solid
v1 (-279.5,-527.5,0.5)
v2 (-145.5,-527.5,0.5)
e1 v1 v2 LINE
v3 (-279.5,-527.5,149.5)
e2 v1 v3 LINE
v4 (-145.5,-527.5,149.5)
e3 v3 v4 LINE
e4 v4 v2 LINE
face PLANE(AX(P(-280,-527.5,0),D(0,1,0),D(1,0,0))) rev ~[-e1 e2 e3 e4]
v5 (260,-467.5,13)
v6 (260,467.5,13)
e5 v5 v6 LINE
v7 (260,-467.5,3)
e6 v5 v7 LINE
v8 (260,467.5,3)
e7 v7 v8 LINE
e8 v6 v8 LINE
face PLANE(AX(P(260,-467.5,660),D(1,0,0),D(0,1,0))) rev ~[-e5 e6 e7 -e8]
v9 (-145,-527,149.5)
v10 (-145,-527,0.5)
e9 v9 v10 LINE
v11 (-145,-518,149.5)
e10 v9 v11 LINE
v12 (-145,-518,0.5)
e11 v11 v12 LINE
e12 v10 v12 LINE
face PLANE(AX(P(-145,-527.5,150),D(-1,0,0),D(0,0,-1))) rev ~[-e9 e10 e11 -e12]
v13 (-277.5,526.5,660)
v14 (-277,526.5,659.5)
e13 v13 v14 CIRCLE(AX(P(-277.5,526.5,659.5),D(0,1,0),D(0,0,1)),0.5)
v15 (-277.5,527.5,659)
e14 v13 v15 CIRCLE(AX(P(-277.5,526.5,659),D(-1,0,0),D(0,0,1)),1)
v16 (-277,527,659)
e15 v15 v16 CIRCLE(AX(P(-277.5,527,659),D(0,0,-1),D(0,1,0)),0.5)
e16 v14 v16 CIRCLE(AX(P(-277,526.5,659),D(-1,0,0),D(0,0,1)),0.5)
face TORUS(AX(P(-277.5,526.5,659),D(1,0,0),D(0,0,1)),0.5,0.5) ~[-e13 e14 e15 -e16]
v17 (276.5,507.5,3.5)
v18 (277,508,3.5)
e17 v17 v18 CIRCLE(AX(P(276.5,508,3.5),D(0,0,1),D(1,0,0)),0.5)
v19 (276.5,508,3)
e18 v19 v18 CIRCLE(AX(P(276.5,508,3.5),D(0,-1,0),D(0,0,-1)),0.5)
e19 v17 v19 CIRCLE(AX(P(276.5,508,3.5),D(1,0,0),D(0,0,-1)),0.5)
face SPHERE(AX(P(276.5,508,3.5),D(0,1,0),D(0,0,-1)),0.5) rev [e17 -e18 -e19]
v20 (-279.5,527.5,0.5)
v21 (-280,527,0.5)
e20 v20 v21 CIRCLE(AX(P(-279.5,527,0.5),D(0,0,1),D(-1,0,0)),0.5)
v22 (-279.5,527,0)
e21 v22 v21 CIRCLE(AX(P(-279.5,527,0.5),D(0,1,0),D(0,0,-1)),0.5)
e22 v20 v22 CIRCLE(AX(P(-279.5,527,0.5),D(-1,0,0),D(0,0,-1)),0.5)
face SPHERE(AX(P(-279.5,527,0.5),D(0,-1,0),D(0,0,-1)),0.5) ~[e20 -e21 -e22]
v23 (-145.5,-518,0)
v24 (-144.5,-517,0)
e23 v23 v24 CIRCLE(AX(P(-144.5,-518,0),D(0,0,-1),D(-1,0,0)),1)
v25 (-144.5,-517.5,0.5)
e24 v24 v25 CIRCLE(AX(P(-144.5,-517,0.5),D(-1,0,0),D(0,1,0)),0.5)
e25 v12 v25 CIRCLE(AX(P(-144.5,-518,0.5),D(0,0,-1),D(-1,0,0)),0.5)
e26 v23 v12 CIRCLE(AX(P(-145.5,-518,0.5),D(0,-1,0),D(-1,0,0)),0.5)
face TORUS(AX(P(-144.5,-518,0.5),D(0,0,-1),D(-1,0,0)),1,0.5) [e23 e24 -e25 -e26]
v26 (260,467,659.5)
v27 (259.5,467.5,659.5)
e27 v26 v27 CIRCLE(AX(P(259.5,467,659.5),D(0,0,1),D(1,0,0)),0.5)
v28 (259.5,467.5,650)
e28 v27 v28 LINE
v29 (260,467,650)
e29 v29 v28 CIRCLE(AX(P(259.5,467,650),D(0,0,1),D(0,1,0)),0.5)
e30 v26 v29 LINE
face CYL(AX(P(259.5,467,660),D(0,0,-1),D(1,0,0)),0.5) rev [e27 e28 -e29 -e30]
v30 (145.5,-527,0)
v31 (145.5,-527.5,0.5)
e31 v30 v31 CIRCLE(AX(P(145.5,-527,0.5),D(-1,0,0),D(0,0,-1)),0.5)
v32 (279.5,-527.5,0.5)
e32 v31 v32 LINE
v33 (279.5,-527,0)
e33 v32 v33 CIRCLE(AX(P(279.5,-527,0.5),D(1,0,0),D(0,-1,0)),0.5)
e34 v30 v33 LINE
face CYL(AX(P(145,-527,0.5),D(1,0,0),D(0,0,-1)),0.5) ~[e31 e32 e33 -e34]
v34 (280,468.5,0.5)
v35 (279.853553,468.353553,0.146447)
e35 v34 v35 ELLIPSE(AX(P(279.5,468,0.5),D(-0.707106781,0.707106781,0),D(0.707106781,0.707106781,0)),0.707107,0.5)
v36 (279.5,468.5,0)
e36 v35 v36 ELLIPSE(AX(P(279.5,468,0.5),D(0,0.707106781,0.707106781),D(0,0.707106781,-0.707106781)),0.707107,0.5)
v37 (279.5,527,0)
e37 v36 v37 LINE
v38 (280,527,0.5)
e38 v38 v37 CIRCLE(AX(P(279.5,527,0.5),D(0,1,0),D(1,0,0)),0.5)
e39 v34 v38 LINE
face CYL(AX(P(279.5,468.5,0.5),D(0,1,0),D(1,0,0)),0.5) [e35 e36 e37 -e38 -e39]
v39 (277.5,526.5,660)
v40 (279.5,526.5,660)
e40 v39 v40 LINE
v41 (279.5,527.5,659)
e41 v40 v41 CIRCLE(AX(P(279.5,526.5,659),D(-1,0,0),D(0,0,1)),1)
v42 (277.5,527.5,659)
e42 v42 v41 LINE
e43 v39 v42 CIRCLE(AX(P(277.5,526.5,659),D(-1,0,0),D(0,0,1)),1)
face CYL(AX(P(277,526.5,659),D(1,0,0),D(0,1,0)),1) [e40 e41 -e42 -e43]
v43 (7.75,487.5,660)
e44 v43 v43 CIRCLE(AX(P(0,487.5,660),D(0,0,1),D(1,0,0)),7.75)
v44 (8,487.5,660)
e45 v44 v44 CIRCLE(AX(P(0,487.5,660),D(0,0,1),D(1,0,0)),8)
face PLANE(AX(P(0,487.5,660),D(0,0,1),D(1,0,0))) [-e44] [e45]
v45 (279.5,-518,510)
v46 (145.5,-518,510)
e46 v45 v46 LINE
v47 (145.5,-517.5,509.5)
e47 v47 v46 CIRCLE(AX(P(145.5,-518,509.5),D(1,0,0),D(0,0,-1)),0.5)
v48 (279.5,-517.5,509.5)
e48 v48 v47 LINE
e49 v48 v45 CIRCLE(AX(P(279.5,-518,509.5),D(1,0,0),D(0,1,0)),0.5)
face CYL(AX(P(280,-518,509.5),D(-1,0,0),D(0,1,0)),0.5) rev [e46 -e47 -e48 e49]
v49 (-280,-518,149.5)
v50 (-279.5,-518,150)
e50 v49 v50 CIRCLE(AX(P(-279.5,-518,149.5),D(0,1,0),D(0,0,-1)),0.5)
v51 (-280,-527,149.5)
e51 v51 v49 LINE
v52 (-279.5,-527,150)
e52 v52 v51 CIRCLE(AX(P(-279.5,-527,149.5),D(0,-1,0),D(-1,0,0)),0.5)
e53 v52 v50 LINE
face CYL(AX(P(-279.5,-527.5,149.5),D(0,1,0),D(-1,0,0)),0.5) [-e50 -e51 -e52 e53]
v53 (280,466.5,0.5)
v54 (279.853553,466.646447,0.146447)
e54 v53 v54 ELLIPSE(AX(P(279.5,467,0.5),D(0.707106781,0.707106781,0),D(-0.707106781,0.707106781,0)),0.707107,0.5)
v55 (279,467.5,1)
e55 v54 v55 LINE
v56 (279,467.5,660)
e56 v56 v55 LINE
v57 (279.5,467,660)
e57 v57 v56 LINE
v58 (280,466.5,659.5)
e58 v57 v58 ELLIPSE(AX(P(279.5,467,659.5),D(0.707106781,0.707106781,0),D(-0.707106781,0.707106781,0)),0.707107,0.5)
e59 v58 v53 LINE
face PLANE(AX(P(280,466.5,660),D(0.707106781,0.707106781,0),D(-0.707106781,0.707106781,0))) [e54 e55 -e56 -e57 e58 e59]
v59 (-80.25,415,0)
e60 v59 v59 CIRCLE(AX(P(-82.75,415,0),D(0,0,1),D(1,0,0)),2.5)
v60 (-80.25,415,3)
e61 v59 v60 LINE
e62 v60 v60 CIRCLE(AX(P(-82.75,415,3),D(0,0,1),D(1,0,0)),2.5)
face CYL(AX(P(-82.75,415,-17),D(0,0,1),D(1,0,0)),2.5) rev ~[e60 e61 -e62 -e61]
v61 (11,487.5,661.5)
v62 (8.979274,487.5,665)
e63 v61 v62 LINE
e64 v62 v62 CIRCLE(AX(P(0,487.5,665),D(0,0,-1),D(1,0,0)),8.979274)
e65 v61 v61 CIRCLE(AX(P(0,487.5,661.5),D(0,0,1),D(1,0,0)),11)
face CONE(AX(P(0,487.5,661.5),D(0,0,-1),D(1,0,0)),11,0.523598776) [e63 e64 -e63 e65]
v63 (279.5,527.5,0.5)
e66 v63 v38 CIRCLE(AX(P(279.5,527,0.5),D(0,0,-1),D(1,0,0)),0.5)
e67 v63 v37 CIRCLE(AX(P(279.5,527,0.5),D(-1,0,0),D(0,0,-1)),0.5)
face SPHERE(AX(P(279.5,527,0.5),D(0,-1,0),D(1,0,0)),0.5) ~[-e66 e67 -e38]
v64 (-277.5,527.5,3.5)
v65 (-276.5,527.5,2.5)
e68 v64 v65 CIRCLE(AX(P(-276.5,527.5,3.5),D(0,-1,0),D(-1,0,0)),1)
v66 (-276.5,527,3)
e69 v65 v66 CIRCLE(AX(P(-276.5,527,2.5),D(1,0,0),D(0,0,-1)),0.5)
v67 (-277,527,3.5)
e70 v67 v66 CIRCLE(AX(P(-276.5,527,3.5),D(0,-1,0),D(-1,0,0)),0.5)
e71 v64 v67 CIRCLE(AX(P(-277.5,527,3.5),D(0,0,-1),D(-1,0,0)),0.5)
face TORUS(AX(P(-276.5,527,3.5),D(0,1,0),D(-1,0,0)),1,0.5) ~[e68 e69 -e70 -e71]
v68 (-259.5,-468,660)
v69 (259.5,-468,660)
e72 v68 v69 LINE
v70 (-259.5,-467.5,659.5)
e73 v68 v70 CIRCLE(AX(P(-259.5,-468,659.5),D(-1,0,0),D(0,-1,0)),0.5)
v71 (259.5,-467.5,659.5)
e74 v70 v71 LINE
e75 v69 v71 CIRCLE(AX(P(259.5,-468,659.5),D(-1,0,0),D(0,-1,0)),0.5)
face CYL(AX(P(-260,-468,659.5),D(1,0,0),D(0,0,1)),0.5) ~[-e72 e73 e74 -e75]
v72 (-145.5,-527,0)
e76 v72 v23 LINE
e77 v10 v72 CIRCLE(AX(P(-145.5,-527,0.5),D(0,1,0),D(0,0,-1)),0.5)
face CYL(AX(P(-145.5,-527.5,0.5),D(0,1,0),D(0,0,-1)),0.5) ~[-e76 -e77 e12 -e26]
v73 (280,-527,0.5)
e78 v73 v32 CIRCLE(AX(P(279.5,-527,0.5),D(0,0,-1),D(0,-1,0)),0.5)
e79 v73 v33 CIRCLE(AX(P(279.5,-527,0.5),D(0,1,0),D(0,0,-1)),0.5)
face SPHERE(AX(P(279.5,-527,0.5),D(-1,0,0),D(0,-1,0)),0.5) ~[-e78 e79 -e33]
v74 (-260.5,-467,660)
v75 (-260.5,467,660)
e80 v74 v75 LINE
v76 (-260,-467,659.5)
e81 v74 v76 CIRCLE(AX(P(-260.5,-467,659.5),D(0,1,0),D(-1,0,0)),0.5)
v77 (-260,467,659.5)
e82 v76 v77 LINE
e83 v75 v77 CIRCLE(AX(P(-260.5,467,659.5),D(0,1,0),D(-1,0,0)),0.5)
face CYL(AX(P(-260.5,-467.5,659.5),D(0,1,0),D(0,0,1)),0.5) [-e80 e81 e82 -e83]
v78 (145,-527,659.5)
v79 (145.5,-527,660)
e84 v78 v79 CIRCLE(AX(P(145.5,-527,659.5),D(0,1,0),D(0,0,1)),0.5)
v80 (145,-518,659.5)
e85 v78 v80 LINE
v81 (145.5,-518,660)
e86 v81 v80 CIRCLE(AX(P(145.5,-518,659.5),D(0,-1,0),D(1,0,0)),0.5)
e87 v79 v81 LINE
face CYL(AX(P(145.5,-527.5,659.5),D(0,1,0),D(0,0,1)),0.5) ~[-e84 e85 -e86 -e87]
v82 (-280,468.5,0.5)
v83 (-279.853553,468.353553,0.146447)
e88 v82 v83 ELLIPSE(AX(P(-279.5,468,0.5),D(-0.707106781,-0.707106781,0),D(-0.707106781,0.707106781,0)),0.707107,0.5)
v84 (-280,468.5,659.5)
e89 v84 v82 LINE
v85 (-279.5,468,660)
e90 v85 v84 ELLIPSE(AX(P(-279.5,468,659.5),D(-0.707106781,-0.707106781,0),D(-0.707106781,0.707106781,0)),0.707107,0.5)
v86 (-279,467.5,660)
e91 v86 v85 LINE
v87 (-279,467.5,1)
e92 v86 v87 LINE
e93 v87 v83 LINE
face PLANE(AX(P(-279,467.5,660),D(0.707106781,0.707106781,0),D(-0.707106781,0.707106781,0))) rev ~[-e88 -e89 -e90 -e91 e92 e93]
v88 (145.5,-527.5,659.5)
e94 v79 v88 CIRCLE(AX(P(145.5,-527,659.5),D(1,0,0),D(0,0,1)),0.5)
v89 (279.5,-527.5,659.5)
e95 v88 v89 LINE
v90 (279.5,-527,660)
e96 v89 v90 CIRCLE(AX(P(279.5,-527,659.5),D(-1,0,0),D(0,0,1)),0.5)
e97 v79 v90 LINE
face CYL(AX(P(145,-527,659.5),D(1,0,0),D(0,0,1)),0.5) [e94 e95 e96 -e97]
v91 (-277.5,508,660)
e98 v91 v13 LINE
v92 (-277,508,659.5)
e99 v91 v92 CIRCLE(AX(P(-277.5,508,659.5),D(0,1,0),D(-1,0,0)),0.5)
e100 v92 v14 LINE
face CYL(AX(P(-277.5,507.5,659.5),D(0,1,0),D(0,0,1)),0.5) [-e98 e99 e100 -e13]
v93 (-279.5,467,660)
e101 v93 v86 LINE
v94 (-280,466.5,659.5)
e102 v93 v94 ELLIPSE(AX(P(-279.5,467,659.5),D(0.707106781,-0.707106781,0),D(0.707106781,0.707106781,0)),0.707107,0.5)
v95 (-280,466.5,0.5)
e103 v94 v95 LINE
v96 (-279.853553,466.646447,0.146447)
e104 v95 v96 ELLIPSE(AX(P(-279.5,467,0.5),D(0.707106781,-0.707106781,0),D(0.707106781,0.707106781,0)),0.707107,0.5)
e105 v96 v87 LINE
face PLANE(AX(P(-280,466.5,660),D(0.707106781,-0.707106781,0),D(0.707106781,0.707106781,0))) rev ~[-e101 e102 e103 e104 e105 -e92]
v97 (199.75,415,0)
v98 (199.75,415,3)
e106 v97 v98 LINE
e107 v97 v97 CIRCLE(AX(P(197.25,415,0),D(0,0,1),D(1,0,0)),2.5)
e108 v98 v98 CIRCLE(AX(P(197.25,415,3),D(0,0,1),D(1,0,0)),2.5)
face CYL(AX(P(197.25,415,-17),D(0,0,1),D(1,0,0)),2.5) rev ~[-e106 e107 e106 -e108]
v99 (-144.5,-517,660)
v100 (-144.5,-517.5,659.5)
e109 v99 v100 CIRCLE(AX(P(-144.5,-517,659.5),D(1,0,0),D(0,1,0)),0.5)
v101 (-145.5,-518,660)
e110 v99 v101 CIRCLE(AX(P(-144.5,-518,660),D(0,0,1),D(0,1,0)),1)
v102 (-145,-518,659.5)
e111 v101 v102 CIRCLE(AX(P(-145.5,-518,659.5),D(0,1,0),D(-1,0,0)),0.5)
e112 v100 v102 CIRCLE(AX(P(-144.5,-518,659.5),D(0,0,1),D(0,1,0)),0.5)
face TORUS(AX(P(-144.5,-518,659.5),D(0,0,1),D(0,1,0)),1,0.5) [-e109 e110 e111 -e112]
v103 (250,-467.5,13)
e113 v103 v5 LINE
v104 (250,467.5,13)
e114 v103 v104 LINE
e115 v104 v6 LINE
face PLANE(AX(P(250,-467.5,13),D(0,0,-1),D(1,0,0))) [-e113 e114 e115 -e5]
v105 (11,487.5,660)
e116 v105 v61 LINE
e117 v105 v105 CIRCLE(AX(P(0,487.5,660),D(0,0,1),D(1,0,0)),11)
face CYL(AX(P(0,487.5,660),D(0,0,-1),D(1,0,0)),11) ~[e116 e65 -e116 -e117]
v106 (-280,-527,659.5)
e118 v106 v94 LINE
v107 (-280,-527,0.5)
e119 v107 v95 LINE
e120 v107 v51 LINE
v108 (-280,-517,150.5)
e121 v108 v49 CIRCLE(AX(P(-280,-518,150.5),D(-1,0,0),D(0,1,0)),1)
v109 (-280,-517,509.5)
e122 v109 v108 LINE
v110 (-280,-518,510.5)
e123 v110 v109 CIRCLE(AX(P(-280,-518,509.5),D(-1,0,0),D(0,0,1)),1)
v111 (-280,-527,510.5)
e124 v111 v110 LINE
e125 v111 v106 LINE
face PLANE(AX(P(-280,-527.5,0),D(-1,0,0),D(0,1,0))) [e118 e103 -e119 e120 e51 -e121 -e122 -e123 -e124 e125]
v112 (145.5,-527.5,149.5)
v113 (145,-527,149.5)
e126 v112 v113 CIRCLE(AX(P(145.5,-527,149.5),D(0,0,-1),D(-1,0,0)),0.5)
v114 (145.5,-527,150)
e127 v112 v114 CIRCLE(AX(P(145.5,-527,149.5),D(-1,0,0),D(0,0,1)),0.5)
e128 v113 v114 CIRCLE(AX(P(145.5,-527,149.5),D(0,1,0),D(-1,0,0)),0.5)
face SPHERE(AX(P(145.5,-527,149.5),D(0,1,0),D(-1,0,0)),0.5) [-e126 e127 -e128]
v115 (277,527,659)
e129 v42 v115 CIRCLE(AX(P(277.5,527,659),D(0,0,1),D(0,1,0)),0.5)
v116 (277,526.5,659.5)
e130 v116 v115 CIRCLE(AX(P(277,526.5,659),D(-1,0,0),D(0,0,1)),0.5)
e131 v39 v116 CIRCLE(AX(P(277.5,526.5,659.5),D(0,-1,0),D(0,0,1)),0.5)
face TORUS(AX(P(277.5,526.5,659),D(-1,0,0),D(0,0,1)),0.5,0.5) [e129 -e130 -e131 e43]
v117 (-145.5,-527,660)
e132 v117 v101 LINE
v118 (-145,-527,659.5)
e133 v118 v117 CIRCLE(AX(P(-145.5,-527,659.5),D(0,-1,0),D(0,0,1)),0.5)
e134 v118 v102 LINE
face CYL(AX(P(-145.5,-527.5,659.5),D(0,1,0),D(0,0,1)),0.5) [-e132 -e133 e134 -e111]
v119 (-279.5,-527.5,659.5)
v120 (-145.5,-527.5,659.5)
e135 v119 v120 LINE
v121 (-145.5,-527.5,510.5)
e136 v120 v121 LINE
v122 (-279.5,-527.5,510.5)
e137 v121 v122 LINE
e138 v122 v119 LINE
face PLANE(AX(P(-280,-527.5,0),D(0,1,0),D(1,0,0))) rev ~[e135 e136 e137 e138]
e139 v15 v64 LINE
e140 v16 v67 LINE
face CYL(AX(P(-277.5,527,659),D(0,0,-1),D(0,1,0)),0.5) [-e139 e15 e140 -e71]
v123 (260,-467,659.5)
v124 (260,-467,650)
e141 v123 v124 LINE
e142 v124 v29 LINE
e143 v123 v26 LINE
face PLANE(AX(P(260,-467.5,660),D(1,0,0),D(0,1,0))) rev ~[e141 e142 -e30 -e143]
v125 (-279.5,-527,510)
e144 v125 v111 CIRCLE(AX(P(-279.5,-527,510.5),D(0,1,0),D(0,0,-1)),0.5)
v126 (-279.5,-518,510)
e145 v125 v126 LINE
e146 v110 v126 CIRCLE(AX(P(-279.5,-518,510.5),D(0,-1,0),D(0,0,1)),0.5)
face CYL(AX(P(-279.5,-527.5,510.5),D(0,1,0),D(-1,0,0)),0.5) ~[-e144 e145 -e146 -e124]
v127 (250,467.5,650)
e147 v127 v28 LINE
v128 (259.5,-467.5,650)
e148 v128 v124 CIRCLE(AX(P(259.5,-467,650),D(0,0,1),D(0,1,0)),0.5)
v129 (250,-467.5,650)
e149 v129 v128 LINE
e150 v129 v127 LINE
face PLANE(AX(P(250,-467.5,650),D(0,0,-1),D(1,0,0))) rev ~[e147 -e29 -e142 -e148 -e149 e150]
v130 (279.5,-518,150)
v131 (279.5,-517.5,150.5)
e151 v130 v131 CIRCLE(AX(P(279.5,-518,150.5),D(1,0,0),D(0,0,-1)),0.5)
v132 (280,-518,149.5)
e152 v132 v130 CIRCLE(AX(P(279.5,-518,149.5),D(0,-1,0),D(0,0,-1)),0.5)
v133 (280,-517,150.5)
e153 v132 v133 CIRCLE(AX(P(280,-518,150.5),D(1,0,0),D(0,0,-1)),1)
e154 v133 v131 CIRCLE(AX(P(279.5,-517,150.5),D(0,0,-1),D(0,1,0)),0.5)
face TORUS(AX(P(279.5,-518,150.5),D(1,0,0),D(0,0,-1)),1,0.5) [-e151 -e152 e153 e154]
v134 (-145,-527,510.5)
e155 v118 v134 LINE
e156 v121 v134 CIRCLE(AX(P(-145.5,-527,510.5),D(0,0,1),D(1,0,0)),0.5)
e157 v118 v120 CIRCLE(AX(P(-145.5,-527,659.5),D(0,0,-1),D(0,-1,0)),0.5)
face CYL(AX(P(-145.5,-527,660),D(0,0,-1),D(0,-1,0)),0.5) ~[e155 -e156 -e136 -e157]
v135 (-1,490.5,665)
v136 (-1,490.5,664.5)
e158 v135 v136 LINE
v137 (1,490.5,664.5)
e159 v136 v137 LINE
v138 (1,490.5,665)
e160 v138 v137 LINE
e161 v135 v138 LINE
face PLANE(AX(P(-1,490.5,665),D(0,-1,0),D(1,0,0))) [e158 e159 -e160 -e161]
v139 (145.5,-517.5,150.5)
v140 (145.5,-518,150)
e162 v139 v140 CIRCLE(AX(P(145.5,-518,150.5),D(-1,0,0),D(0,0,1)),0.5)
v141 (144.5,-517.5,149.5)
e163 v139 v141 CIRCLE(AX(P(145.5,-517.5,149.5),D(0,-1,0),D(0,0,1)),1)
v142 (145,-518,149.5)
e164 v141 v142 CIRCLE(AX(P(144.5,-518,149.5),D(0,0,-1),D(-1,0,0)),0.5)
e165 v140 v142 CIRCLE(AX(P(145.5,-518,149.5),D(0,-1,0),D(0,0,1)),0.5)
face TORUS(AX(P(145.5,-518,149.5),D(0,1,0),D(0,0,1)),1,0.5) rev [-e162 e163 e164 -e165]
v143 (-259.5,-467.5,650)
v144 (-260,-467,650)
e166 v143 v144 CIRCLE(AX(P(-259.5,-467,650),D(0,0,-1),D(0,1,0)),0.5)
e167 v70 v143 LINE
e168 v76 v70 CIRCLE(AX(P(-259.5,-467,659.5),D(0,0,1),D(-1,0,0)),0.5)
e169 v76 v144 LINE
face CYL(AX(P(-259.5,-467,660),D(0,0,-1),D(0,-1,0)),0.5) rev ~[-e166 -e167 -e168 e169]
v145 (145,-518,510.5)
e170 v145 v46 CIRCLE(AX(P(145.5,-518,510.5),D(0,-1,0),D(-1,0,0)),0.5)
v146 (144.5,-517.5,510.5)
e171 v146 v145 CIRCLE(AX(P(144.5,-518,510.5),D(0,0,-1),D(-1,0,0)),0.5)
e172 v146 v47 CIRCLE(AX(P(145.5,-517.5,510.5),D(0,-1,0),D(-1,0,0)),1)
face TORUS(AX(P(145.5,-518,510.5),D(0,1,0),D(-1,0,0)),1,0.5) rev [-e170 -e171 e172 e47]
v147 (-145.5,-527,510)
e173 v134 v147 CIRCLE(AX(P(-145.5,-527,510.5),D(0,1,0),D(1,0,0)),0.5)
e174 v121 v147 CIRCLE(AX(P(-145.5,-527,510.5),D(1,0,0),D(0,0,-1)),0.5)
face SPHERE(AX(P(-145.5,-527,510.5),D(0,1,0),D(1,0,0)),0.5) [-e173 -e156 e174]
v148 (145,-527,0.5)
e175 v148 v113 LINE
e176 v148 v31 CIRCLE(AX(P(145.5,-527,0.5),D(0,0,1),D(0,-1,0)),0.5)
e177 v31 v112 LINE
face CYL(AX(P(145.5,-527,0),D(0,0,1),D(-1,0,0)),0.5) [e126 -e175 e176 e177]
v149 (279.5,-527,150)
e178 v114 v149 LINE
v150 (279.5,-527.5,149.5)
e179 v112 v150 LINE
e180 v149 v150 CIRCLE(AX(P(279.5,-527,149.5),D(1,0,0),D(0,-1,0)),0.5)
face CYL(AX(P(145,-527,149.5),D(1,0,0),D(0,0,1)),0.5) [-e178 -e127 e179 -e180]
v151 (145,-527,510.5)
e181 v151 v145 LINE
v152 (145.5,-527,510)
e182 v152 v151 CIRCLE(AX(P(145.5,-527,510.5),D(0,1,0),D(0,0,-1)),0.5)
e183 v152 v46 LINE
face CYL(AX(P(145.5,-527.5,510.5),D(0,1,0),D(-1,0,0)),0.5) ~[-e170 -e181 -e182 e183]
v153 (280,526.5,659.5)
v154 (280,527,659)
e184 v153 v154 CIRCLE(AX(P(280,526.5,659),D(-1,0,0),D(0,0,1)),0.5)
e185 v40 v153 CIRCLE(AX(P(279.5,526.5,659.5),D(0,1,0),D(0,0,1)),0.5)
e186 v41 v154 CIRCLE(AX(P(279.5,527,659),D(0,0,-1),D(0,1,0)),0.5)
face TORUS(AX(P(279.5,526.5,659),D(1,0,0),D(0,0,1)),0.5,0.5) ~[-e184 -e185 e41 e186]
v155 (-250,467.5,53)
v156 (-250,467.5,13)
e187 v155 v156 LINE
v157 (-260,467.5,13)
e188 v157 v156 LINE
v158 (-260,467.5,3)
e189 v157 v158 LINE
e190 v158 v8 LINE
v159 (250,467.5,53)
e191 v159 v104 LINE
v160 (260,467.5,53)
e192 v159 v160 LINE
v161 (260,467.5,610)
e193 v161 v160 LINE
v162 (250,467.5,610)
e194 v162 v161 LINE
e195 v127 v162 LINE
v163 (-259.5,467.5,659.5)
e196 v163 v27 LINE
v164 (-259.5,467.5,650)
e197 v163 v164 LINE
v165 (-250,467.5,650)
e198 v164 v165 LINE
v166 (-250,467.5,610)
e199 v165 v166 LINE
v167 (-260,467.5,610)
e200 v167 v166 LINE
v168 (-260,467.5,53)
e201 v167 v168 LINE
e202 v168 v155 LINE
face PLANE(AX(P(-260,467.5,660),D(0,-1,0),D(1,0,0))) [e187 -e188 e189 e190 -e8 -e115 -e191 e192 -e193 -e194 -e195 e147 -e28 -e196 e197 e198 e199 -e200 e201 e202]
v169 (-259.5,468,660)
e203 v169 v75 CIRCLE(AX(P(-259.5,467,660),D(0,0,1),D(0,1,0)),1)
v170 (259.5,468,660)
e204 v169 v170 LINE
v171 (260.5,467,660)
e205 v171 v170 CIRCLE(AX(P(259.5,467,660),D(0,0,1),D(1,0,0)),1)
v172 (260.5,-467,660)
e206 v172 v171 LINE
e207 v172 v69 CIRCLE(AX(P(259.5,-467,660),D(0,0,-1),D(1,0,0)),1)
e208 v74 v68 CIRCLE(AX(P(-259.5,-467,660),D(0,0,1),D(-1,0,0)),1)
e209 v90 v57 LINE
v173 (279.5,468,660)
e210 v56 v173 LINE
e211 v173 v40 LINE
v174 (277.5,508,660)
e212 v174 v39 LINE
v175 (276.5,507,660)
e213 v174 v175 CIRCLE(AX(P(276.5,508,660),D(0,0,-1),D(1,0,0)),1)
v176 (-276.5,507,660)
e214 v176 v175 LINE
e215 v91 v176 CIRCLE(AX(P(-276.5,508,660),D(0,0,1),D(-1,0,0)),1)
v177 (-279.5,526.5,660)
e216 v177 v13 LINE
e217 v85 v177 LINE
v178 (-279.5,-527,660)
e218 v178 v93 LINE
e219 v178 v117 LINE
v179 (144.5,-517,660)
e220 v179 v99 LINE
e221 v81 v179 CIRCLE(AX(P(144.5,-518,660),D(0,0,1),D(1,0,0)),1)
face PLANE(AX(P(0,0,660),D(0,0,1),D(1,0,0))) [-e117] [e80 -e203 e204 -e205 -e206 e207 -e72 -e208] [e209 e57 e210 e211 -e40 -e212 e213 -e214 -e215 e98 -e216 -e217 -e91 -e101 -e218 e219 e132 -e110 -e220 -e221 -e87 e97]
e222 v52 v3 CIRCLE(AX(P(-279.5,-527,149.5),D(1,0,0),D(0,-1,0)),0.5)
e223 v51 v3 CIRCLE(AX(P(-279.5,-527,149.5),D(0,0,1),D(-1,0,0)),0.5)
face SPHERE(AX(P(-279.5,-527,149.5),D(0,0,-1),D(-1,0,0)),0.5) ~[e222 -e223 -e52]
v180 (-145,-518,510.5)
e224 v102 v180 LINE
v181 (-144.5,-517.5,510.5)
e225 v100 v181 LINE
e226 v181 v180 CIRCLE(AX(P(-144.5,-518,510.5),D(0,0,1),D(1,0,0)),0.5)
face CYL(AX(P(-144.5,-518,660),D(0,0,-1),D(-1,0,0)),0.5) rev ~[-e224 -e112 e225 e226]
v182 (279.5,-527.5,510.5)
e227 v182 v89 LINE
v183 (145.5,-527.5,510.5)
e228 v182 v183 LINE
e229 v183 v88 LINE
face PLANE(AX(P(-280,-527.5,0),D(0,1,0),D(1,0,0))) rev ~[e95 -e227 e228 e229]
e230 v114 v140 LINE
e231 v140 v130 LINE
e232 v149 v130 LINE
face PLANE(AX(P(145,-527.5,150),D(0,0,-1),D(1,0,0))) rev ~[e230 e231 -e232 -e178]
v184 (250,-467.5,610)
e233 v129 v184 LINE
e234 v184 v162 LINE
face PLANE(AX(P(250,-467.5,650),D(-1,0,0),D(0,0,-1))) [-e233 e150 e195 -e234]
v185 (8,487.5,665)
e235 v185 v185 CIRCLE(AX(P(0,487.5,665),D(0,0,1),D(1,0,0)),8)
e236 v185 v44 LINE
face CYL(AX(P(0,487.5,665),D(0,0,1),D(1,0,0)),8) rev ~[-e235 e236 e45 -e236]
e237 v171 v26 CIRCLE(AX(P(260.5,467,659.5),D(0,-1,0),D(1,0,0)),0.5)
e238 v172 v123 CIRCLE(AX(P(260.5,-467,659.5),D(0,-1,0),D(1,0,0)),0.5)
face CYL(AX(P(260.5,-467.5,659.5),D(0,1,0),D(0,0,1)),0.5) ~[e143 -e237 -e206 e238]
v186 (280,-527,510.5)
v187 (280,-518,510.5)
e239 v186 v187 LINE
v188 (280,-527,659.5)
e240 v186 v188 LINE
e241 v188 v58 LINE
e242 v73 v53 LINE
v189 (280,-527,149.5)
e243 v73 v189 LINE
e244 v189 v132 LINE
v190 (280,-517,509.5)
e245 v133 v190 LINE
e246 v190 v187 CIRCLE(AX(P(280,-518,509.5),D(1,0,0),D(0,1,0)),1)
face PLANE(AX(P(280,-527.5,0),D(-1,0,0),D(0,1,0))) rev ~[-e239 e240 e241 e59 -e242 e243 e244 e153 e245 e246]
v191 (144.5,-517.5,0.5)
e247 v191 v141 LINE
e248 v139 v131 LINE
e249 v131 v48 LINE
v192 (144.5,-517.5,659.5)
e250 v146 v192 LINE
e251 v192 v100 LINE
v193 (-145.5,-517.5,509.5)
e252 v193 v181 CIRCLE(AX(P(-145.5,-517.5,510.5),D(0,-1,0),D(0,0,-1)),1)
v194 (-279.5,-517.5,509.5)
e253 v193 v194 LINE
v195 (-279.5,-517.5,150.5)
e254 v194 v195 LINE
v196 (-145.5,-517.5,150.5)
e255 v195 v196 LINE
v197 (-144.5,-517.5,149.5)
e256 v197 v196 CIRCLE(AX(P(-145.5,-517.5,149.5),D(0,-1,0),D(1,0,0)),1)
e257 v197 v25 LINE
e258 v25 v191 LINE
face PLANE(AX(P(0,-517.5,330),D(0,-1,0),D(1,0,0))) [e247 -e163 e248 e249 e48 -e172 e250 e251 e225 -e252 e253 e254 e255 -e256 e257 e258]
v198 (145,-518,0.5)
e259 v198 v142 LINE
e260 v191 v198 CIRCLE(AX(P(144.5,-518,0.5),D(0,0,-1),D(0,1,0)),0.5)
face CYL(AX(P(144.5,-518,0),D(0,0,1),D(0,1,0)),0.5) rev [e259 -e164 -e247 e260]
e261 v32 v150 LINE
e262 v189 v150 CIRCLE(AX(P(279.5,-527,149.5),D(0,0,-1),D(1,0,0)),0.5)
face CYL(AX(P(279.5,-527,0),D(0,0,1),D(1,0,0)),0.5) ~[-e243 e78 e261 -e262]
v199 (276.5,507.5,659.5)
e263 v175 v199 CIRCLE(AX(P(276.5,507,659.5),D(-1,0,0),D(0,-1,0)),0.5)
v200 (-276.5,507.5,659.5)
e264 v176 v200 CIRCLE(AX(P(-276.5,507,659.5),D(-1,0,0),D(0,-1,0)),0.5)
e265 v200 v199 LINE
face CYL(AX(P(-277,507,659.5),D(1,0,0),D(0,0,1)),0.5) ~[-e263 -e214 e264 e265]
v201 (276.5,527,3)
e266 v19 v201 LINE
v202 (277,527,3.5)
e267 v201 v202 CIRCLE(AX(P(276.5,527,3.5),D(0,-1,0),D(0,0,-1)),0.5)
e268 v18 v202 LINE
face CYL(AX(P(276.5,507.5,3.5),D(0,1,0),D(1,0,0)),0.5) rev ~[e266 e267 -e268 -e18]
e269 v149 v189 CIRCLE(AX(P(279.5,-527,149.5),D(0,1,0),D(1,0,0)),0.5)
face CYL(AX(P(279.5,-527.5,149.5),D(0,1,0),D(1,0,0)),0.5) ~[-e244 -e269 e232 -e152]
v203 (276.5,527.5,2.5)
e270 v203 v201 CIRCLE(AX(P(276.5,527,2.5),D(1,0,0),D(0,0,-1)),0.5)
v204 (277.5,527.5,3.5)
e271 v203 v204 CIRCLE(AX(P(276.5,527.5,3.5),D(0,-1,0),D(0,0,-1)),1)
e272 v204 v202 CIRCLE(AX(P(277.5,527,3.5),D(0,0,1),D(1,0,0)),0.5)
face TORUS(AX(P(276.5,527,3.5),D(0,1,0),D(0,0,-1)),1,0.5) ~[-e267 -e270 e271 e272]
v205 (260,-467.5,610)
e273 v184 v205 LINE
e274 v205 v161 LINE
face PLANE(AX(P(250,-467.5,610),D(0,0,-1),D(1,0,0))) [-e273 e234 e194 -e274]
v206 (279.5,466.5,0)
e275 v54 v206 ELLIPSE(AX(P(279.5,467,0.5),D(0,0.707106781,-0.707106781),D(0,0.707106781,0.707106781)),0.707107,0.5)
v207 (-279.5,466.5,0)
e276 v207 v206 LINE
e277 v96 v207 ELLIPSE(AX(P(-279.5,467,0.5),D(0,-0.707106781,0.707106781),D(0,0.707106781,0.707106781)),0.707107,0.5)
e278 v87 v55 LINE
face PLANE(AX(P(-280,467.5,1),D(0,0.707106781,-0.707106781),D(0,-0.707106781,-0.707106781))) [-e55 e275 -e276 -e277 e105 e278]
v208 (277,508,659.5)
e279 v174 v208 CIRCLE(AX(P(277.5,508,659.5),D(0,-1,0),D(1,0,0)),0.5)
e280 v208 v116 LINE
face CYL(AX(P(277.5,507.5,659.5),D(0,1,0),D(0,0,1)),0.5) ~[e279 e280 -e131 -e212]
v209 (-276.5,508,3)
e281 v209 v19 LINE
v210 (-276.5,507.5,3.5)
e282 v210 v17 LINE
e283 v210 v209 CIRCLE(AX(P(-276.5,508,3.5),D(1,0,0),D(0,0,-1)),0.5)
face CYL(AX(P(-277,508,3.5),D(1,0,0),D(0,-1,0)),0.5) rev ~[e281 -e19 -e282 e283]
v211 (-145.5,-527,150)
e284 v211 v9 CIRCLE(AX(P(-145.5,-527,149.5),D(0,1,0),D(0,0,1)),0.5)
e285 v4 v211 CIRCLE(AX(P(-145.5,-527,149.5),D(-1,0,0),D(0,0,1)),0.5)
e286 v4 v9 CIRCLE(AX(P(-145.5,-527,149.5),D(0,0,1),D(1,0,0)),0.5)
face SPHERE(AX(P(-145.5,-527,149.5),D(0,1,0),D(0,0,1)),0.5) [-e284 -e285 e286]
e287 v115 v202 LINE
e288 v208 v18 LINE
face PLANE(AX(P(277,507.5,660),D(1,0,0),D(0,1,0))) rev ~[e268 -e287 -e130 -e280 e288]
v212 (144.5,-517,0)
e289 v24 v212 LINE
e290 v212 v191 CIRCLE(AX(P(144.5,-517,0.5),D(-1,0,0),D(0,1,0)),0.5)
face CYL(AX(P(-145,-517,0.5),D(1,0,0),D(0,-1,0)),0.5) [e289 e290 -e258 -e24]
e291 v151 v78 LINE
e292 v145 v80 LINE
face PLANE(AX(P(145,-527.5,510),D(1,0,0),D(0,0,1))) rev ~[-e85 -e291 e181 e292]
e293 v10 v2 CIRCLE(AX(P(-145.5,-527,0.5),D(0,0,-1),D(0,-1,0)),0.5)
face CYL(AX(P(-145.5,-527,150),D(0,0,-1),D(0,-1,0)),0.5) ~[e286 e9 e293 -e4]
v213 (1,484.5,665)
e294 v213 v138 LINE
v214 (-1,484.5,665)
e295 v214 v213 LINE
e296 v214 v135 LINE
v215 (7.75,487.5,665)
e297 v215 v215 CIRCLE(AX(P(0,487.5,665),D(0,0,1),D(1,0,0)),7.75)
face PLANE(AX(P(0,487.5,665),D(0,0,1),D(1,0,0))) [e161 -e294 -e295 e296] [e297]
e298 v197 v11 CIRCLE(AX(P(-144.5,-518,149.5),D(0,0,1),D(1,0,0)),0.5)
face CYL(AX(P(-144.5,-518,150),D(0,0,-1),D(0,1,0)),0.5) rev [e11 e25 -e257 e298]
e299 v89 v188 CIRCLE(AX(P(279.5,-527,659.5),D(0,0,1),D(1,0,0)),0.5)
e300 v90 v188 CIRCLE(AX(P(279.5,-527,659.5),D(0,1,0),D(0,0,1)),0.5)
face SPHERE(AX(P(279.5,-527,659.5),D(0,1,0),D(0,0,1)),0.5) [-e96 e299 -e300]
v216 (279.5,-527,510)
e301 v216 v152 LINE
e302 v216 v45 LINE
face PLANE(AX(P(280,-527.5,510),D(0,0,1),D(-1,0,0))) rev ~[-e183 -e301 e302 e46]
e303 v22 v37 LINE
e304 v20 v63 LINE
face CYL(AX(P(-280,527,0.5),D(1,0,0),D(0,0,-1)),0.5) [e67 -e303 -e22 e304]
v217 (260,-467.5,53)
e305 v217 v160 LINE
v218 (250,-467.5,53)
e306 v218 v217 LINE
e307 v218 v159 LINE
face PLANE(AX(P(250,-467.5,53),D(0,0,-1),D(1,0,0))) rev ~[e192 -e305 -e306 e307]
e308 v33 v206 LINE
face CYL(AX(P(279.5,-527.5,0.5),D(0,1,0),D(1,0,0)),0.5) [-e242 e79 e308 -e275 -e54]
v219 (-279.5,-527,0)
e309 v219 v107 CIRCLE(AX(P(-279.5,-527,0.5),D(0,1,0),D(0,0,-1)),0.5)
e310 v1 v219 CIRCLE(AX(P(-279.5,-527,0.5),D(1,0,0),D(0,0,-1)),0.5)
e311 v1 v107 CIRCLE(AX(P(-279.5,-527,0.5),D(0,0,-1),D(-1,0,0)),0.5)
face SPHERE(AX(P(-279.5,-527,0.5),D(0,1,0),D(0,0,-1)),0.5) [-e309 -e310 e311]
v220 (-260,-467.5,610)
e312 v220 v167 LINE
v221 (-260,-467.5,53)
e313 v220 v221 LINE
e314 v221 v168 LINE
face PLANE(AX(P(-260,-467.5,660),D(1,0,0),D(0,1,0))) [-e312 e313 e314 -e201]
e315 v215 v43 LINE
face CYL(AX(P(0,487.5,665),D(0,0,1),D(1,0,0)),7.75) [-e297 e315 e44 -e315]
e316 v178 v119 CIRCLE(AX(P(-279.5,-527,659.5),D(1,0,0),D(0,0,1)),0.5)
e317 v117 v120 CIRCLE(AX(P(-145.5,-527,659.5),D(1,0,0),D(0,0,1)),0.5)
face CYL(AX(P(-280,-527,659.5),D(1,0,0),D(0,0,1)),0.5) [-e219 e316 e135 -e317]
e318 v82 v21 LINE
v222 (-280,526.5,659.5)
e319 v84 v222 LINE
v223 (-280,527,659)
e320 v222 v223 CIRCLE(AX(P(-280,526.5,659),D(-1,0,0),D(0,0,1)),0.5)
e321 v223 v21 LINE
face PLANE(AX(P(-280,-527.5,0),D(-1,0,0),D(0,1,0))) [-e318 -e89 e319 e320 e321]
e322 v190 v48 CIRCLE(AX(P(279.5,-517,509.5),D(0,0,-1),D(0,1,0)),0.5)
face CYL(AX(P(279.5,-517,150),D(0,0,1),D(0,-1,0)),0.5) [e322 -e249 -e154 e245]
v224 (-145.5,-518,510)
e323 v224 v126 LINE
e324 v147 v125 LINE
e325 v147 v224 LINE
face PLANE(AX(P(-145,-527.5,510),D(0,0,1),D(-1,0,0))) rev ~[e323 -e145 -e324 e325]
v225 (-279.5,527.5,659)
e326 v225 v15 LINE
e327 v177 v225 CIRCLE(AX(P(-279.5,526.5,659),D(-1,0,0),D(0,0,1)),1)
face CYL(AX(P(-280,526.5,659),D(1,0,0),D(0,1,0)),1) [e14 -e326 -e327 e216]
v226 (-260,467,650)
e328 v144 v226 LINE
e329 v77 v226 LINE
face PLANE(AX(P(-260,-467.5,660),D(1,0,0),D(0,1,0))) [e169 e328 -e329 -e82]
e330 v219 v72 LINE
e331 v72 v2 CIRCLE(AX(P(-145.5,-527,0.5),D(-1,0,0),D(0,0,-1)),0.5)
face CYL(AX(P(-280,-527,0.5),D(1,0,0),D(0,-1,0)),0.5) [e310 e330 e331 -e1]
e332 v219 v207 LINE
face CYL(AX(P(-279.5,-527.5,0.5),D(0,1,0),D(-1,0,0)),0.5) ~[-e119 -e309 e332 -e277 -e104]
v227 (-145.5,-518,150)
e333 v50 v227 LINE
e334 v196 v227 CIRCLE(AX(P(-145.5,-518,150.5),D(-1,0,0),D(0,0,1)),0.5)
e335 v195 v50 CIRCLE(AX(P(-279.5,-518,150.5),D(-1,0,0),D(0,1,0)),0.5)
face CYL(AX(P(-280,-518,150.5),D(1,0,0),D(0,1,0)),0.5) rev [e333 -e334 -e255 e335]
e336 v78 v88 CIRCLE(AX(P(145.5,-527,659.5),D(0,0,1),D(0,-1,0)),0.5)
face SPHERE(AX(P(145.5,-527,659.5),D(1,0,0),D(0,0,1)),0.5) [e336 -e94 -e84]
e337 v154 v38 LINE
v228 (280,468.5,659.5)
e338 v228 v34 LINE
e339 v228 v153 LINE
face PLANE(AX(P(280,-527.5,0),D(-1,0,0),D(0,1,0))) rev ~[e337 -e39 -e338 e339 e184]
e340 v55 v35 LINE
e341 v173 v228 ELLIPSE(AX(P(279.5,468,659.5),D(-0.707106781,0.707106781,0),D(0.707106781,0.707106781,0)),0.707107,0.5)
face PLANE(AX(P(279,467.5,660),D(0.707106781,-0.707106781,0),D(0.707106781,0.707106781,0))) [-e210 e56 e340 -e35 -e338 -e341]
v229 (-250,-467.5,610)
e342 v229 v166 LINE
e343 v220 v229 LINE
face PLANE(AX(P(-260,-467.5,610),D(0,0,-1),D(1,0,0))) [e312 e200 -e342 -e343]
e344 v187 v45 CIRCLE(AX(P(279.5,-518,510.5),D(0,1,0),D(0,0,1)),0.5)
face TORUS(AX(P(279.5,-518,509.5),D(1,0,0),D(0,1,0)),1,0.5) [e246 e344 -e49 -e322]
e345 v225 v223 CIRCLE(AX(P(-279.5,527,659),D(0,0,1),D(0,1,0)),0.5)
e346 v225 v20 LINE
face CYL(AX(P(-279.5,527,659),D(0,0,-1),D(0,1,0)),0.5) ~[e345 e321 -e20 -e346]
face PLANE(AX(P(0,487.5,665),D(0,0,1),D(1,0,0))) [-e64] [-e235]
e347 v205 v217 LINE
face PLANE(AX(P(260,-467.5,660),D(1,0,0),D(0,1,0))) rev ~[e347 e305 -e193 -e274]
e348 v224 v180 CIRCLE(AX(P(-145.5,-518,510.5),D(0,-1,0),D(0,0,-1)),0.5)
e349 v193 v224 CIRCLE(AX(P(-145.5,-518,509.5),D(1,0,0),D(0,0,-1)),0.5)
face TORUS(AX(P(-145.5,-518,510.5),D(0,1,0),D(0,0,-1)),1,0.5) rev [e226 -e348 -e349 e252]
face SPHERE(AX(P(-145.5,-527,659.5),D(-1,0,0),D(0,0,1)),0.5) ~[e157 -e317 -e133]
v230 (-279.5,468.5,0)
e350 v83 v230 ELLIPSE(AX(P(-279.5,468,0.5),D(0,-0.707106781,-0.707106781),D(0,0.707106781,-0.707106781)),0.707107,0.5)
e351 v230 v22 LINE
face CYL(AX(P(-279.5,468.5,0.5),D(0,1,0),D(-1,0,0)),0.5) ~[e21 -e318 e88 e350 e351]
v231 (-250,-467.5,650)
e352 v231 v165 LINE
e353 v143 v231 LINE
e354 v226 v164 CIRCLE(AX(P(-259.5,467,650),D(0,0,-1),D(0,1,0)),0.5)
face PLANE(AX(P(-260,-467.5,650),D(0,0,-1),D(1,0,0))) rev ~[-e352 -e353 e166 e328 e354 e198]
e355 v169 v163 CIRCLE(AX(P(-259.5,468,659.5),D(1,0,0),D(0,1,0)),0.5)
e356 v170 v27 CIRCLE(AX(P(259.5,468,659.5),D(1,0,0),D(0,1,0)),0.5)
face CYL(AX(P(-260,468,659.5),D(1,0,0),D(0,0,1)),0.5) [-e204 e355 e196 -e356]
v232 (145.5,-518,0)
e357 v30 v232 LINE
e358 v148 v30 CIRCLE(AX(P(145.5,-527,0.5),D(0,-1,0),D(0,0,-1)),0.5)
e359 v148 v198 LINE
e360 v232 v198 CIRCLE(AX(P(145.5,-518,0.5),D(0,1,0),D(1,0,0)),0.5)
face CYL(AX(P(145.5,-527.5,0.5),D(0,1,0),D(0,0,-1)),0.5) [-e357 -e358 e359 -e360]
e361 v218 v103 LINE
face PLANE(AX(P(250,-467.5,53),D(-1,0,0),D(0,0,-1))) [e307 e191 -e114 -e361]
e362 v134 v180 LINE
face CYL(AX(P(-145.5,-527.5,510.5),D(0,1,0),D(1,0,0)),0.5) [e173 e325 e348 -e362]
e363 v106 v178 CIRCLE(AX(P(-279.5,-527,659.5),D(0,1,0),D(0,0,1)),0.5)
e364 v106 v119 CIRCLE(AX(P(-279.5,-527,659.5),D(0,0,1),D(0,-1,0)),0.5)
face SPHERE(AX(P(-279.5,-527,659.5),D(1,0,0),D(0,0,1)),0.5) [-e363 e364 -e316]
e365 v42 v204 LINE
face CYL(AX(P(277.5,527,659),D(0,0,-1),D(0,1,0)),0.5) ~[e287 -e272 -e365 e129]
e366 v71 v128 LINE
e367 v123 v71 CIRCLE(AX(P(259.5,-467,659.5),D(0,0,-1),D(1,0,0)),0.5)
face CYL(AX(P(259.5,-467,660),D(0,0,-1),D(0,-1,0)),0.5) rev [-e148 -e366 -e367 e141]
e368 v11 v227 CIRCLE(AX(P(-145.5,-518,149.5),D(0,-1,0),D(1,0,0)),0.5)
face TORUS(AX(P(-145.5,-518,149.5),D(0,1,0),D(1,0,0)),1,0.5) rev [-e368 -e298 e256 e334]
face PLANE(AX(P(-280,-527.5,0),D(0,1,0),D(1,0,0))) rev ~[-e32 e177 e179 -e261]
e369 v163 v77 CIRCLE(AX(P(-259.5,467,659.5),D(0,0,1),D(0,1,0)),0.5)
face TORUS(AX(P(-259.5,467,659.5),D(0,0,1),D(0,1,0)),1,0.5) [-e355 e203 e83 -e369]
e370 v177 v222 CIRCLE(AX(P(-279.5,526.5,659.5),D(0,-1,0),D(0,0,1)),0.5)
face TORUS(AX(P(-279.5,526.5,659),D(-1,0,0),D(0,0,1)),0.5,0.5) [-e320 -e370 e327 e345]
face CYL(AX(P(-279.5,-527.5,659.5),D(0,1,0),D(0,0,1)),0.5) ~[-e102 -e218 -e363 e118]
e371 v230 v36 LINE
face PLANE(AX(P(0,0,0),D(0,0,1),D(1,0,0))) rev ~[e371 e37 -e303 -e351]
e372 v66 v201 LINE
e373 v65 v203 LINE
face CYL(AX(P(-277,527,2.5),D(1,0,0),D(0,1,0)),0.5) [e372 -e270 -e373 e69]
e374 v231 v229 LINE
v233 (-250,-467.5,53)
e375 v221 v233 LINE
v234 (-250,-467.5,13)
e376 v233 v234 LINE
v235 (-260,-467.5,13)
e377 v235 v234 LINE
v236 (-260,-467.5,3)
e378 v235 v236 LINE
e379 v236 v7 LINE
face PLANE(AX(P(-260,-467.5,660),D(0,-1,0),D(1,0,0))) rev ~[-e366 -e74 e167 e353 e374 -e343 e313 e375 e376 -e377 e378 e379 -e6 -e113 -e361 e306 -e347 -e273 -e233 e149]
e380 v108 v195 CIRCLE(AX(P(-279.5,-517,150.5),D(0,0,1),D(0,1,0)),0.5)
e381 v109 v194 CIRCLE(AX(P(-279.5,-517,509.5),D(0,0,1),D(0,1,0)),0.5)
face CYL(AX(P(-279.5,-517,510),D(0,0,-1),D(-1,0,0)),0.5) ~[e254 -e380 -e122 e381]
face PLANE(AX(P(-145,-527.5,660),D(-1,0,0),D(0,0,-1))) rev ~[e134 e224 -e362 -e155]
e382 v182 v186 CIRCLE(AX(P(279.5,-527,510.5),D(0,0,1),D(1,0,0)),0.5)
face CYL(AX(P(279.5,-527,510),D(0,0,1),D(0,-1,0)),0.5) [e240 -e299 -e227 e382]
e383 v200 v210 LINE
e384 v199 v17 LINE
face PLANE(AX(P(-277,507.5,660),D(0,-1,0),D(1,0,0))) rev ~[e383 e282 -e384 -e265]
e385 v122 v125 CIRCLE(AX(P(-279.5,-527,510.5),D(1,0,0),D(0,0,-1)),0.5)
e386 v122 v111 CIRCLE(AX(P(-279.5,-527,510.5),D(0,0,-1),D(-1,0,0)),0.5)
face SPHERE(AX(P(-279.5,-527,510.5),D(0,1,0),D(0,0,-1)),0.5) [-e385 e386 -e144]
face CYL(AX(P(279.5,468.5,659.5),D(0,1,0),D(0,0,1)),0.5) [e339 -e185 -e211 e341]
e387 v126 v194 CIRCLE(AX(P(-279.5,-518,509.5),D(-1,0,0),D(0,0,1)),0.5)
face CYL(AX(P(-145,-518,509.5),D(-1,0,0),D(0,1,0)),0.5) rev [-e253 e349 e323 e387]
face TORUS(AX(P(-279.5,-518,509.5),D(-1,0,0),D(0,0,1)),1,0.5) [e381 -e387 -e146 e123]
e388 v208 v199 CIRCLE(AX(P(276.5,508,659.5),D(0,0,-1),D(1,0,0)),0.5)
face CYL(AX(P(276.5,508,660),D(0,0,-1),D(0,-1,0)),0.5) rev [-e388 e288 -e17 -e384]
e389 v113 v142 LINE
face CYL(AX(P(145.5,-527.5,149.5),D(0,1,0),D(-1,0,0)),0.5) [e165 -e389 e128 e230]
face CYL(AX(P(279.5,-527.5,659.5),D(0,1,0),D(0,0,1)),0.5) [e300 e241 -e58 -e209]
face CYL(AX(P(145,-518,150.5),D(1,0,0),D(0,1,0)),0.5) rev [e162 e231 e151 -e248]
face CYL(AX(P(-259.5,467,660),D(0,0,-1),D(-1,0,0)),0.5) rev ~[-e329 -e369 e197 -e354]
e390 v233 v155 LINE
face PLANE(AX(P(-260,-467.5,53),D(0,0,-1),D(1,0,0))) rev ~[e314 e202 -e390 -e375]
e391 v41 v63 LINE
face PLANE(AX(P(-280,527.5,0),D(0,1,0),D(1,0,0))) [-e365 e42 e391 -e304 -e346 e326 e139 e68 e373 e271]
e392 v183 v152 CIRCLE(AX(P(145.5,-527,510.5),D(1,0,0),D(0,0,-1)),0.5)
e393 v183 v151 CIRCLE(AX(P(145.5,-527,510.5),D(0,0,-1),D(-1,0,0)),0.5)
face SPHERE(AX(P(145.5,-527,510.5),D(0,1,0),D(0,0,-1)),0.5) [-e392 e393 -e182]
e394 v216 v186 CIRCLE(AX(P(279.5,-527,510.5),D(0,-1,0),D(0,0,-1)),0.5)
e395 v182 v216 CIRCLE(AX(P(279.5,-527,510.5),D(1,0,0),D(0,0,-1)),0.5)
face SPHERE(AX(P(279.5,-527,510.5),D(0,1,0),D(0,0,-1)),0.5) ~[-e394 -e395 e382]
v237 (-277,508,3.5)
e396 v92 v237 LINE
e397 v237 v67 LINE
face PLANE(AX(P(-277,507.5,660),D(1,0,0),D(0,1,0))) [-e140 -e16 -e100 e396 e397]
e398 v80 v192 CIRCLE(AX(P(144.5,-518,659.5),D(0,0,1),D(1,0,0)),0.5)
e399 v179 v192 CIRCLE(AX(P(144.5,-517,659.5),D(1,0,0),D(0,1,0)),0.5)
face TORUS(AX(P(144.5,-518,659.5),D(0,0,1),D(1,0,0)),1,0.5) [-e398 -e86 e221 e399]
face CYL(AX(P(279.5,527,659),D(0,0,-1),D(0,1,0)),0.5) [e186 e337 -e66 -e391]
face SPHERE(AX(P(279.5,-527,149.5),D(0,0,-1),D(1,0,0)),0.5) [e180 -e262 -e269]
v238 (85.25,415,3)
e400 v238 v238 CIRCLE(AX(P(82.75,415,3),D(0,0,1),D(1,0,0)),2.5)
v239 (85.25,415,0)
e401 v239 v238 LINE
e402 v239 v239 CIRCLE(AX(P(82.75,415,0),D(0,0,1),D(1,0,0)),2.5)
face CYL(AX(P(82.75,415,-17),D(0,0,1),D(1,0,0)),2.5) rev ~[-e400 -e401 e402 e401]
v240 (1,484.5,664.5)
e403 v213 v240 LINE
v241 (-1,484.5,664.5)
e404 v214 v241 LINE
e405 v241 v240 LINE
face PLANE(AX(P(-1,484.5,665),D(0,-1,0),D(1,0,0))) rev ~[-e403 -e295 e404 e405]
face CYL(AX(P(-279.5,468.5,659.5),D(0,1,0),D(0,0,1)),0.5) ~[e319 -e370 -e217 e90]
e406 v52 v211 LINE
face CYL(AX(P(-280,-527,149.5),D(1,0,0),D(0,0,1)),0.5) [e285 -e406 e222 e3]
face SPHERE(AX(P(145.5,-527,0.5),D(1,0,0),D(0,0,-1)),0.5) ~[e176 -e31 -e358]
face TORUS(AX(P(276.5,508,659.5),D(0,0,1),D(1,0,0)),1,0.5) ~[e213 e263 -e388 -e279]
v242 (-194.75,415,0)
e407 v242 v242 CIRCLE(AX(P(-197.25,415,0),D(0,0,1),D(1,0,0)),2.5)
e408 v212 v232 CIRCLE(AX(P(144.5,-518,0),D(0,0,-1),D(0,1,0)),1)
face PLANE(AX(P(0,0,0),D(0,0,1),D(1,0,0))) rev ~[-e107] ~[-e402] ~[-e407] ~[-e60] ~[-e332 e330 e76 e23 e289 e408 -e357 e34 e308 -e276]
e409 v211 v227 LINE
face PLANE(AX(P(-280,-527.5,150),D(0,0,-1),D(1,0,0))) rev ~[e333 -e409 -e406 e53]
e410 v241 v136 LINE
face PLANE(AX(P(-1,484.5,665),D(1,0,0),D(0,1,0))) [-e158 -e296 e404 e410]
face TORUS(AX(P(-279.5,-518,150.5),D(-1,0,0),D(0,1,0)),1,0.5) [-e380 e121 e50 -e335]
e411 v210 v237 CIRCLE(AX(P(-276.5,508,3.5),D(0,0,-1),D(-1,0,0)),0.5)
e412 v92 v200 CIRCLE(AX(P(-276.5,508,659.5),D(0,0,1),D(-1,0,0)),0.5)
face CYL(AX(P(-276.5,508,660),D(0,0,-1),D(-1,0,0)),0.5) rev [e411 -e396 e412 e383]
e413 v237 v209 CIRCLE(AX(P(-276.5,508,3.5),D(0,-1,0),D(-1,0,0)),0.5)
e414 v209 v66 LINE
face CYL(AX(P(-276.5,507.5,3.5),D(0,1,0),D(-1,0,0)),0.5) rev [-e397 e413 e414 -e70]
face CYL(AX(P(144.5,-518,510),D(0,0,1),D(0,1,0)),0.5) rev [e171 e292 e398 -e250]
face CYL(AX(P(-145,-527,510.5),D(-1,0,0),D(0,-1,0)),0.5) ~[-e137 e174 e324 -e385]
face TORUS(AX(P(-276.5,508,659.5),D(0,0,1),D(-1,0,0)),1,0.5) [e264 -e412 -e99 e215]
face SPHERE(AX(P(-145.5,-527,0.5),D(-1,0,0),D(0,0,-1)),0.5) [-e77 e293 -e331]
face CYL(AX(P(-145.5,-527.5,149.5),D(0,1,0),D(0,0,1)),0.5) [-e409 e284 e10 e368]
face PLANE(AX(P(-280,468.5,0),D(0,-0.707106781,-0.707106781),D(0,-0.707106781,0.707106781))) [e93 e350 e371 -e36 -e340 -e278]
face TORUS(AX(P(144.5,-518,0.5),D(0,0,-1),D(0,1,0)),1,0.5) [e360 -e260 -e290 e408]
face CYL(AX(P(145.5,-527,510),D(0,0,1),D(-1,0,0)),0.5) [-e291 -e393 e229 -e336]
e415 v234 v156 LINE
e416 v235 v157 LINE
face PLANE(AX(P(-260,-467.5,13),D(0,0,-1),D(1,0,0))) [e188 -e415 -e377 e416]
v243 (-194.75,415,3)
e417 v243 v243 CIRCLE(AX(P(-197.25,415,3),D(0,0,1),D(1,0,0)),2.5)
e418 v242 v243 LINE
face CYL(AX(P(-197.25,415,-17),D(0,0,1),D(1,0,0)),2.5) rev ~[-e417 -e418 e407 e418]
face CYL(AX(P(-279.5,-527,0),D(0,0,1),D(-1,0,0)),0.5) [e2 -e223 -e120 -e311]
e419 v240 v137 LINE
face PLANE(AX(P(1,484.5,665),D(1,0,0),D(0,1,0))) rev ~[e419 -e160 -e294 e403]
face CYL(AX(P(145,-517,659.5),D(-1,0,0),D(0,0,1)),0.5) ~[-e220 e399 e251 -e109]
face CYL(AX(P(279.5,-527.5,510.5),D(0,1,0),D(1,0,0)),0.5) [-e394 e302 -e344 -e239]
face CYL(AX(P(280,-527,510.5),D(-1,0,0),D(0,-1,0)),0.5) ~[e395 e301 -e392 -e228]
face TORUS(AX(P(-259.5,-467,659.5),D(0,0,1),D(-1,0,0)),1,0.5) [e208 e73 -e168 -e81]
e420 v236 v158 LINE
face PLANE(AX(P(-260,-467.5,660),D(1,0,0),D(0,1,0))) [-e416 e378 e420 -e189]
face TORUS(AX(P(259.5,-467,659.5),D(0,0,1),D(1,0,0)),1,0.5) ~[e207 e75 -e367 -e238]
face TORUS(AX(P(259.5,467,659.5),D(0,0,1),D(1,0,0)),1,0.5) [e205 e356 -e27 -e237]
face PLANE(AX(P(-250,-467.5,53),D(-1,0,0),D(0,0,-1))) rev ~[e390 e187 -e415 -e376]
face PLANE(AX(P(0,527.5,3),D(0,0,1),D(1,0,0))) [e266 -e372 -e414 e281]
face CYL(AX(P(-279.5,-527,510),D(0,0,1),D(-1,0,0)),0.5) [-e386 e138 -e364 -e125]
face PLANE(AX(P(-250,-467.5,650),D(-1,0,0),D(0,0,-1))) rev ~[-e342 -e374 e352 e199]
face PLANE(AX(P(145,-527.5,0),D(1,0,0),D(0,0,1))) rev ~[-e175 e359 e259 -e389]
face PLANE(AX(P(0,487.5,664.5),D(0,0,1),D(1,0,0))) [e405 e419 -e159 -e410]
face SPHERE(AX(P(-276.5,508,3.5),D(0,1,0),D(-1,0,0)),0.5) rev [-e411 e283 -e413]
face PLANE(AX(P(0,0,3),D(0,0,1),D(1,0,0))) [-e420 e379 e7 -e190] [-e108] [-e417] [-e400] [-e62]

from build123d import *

# Parameters (mm, degrees)
SKETCH1_W             = 560
SKETCH1_H             = 1055
BOSS_EXTRUDE1_DEPTH   = 660
SKETCH2_W             = 554
SKETCH2_H             = 40
CUT_EXTRUDE1_DEPTH    = 657
SKETCH3_W             = 520
SKETCH3_H             = 935
CUT_EXTRUDE2_DEPTH    = 657
CUT_EXTRUDE3_DEPTH    = 10
FILETE1_R             = 1
SKETCH5_W             = 10
SKETCH5_H             = 40
BOSS_EXTRUDE2_DEPTH   = 935
CUT_EXTRUDE4_DEPTH    = 891.08777657
CUT_EXTRUDE5_DEPTH    = 1014.635166122
SKETCH9_R             = 11
BOSS_EXTRUDE3_DEPTH   = 1.5
SKETCH10_R            = 11
BOSS_EXTRUDE4_DEPTH   = 3.5
BOSS_EXTRUDE4_TAPER   = 30
SKETCH11_R            = 8
SKETCH11_R_2          = 7.75
CUT_EXTRUDE6_DEPTH    = 5
SKETCH12_W            = 2
SKETCH12_H            = 6
CUT_EXTRUDE7_DEPTH    = 0.5
FILETE2_R             = 0.5
TAPPED_HOLE_M61_D     = 5
TAPPED_HOLE_M61_DEPTH = 17
TAPPED_HOLE_M61_TIP   = 1.502151548


with BuildPart() as part:
    # Sketch1 → Boss-Extrude1 (new body)
    with BuildSketch(Plane.XY):
        Rectangle(SKETCH1_W, SKETCH1_H)
    extrude(amount=BOSS_EXTRUDE1_DEPTH)

    # Sketch2 → Cut-Extrude1 (cut)
    with BuildSketch(Plane.XY.offset(660)):
        with Locations((0, 527.5)):
            Rectangle(SKETCH2_W, SKETCH2_H)
    extrude(amount=-CUT_EXTRUDE1_DEPTH, mode=Mode.SUBTRACT)

    # Sketch3 → Cut-Extrude2 (cut)
    with BuildSketch(Plane.XY.offset(660)):
        Rectangle(SKETCH3_W, SKETCH3_H)
    extrude(amount=-CUT_EXTRUDE2_DEPTH, mode=Mode.SUBTRACT)

    # Sketch4 → Cut-Extrude3 (cut)
    with BuildSketch(Plane.XZ.offset(527.5)):
        Polygon((-145, 660), (-145, 510), (-280, 510), (-280, 150), (-145, 150), (-145, 0), (145, 0), (145, 150), (280, 150), (280, 510), (145, 510), (145, 660), align=None)
    extrude(amount=-CUT_EXTRUDE3_DEPTH, mode=Mode.SUBTRACT)

    # Filete1
    filete1_edges = [part.edges().sort_by_distance(p)[0] for p in [
        (-278.5, 527.5, 660),
        (278.5, 527.5, 660),
    ]]
    fillet(filete1_edges, radius=FILETE1_R)

    # Sketch5 → Boss-Extrude2 (add)
    with BuildSketch(Plane(origin=(0, -467.5, 0), x_dir=(1, 0, 0), z_dir=(0, 1, 0))):
        with Locations((-255, -630)):
            Rectangle(SKETCH5_W, SKETCH5_H)
        with Locations((255, -630)):
            Rectangle(SKETCH5_W, SKETCH5_H)
        with Locations((-255, -33)):
            Rectangle(SKETCH5_W, SKETCH5_H)
        with Locations((255, -33)):
            Rectangle(SKETCH5_W, SKETCH5_H)
    extrude(amount=BOSS_EXTRUDE2_DEPTH)

    # Sketch6 → Cut-Extrude4 (cut, through all)
    with BuildSketch(Plane.XY.offset(660)):
        Polygon((279, 467.5), (280, 468.5), (280, 466.5), align=None)
        Polygon((-279, 467.5), (-280, 468.5), (-280, 466.5), align=None)
    extrude(amount=-CUT_EXTRUDE4_DEPTH, mode=Mode.SUBTRACT)

    # Sketch7 → Cut-Extrude5 (cut, through all)
    with BuildSketch(Plane.ZY.offset(280)):
        Polygon((0, 468.5), (1, 467.5), (0, 466.5), align=None)
    extrude(amount=-CUT_EXTRUDE5_DEPTH, mode=Mode.SUBTRACT)

    # Sketch9 → Boss-Extrude3 (add)
    with BuildSketch(Plane.XY.offset(660)):
        with Locations((0, 487.5)):
            Circle(SKETCH9_R)
    extrude(amount=BOSS_EXTRUDE3_DEPTH)

    # Sketch10 → Boss-Extrude4 (add)
    with BuildSketch(Plane.XY.offset(661.5)):
        with Locations((0, 487.5)):
            Circle(SKETCH10_R)
    extrude(amount=BOSS_EXTRUDE4_DEPTH, taper=BOSS_EXTRUDE4_TAPER)

    # Sketch11 → Cut-Extrude6 (cut)
    with BuildSketch(Plane.XY.offset(665)):
        with Locations((0, 487.5)):
            Circle(SKETCH11_R)
        with Locations((0, 487.5)):
            Circle(SKETCH11_R_2, mode=Mode.SUBTRACT)
    extrude(amount=-CUT_EXTRUDE6_DEPTH, mode=Mode.SUBTRACT)

    # Sketch12 → Cut-Extrude7 (cut)
    with BuildSketch(Plane.XY.offset(665)):
        with Locations((0, 487.5)):
            Rectangle(SKETCH12_W, SKETCH12_H)
    extrude(amount=-CUT_EXTRUDE7_DEPTH, mode=Mode.SUBTRACT)

    # Filete2
    filete2_edges = [part.edges().sort_by_distance(p)[0] for p in [
        (-260, -467.5, 655),
        (260, 467.5, 655),
        (260, -467.5, 655),
        (-212.5, -527.5, 660),
        (280, 498, 0),
        (0, 527.5, 3),
        (280, 497.5, 660),
        (277, 517, 660),
        (-280, -30.5, 0),
        (-280, -30.5, 660),
        (0, 507.5, 660),
        (277, 517.5, 3),
        (277, 527.5, 331),
        (-277, 517.5, 3),
        (-277, 507.5, 331.5),
        (0, 507.5, 3),
        (277, 507.5, 331.5),
        (260, 0, 660),
        (0, 467.5, 660),
        (-260, 0, 660),
        (0, -467.5, 660),
        (280, -30.5, 660),
        (-212.5, -527.5, 0),
        (212.5, -527.5, 0),
        (212.5, -527.5, 660),
        (-280, 498, 0),
        (280, -527.5, 75),
        (-280, -527.5, 75),
        (0, 527.5, 0),
        (280, -30.5, 0),
        (0, -517.5, 660),
        (-145, -522.5, 660),
        (145, -517.5, 585),
        (145, -522.5, 660),
        (212.5, -517.5, 510),
        (145, -522.5, 510),
        (280, -517.5, 330),
        (280, -522.5, 510),
        (212.5, -517.5, 150),
        (280, -522.5, 150),
        (145, -517.5, 75),
        (145, -522.5, 150),
        (0, -517.5, 0),
        (145, -522.5, 0),
        (-145, -517.5, 75),
        (-145, -522.5, 0),
        (-212.5, -517.5, 150),
        (-145, -522.5, 150),
        (-280, -517.5, 330),
        (-280, -522.5, 150),
        (-212.5, -517.5, 510),
        (-280, -522.5, 510),
        (-145, -517.5, 585),
        (-145, -522.5, 510),
        (-145, -527.5, 585),
        (-212.5, -527.5, 510),
        (-212.5, -527.5, 150),
        (-145, -527.5, 75),
        (145, -527.5, 75),
        (212.5, -527.5, 150),
        (212.5, -527.5, 510),
        (145, -527.5, 585),
        (280, -527.5, 585),
        (-280, -527.5, 585),
        (-277, 517, 660),
        (-280, 497.5, 660),
        (277, 527.207106781, 659.707106781),
        (280, 527.5, 329.5),
        (-280, 527.5, 329.5),
        (-277, 527.5, 331),
        (280, 527.207106781, 659.707106781),
        (-280, 527.207106781, 659.707106781),
        (-277, 527.207106781, 659.707106781),
        (-260, 467.5, 655),
    ]]
    fillet(filete2_edges, radius=FILETE2_R)

    # Tapped Hole M61
    with Locations(Plane(origin=(0, 0, 0), x_dir=(-1, 0, 0), z_dir=(0, 0, -1))):
        with Locations((-197.25, 415), (-82.75, 415), (197.25, 415), (82.75, 415)):
            Hole(TAPPED_HOLE_M61_D / 2, depth=TAPPED_HOLE_M61_DEPTH)
            with Locations((0, 0, -(TAPPED_HOLE_M61_DEPTH + TAPPED_HOLE_M61_TIP / 2))):  # 118° drill point
                Cone(0, TAPPED_HOLE_M61_D / 2, TAPPED_HOLE_M61_TIP, mode=Mode.SUBTRACT)


solid = part.part
